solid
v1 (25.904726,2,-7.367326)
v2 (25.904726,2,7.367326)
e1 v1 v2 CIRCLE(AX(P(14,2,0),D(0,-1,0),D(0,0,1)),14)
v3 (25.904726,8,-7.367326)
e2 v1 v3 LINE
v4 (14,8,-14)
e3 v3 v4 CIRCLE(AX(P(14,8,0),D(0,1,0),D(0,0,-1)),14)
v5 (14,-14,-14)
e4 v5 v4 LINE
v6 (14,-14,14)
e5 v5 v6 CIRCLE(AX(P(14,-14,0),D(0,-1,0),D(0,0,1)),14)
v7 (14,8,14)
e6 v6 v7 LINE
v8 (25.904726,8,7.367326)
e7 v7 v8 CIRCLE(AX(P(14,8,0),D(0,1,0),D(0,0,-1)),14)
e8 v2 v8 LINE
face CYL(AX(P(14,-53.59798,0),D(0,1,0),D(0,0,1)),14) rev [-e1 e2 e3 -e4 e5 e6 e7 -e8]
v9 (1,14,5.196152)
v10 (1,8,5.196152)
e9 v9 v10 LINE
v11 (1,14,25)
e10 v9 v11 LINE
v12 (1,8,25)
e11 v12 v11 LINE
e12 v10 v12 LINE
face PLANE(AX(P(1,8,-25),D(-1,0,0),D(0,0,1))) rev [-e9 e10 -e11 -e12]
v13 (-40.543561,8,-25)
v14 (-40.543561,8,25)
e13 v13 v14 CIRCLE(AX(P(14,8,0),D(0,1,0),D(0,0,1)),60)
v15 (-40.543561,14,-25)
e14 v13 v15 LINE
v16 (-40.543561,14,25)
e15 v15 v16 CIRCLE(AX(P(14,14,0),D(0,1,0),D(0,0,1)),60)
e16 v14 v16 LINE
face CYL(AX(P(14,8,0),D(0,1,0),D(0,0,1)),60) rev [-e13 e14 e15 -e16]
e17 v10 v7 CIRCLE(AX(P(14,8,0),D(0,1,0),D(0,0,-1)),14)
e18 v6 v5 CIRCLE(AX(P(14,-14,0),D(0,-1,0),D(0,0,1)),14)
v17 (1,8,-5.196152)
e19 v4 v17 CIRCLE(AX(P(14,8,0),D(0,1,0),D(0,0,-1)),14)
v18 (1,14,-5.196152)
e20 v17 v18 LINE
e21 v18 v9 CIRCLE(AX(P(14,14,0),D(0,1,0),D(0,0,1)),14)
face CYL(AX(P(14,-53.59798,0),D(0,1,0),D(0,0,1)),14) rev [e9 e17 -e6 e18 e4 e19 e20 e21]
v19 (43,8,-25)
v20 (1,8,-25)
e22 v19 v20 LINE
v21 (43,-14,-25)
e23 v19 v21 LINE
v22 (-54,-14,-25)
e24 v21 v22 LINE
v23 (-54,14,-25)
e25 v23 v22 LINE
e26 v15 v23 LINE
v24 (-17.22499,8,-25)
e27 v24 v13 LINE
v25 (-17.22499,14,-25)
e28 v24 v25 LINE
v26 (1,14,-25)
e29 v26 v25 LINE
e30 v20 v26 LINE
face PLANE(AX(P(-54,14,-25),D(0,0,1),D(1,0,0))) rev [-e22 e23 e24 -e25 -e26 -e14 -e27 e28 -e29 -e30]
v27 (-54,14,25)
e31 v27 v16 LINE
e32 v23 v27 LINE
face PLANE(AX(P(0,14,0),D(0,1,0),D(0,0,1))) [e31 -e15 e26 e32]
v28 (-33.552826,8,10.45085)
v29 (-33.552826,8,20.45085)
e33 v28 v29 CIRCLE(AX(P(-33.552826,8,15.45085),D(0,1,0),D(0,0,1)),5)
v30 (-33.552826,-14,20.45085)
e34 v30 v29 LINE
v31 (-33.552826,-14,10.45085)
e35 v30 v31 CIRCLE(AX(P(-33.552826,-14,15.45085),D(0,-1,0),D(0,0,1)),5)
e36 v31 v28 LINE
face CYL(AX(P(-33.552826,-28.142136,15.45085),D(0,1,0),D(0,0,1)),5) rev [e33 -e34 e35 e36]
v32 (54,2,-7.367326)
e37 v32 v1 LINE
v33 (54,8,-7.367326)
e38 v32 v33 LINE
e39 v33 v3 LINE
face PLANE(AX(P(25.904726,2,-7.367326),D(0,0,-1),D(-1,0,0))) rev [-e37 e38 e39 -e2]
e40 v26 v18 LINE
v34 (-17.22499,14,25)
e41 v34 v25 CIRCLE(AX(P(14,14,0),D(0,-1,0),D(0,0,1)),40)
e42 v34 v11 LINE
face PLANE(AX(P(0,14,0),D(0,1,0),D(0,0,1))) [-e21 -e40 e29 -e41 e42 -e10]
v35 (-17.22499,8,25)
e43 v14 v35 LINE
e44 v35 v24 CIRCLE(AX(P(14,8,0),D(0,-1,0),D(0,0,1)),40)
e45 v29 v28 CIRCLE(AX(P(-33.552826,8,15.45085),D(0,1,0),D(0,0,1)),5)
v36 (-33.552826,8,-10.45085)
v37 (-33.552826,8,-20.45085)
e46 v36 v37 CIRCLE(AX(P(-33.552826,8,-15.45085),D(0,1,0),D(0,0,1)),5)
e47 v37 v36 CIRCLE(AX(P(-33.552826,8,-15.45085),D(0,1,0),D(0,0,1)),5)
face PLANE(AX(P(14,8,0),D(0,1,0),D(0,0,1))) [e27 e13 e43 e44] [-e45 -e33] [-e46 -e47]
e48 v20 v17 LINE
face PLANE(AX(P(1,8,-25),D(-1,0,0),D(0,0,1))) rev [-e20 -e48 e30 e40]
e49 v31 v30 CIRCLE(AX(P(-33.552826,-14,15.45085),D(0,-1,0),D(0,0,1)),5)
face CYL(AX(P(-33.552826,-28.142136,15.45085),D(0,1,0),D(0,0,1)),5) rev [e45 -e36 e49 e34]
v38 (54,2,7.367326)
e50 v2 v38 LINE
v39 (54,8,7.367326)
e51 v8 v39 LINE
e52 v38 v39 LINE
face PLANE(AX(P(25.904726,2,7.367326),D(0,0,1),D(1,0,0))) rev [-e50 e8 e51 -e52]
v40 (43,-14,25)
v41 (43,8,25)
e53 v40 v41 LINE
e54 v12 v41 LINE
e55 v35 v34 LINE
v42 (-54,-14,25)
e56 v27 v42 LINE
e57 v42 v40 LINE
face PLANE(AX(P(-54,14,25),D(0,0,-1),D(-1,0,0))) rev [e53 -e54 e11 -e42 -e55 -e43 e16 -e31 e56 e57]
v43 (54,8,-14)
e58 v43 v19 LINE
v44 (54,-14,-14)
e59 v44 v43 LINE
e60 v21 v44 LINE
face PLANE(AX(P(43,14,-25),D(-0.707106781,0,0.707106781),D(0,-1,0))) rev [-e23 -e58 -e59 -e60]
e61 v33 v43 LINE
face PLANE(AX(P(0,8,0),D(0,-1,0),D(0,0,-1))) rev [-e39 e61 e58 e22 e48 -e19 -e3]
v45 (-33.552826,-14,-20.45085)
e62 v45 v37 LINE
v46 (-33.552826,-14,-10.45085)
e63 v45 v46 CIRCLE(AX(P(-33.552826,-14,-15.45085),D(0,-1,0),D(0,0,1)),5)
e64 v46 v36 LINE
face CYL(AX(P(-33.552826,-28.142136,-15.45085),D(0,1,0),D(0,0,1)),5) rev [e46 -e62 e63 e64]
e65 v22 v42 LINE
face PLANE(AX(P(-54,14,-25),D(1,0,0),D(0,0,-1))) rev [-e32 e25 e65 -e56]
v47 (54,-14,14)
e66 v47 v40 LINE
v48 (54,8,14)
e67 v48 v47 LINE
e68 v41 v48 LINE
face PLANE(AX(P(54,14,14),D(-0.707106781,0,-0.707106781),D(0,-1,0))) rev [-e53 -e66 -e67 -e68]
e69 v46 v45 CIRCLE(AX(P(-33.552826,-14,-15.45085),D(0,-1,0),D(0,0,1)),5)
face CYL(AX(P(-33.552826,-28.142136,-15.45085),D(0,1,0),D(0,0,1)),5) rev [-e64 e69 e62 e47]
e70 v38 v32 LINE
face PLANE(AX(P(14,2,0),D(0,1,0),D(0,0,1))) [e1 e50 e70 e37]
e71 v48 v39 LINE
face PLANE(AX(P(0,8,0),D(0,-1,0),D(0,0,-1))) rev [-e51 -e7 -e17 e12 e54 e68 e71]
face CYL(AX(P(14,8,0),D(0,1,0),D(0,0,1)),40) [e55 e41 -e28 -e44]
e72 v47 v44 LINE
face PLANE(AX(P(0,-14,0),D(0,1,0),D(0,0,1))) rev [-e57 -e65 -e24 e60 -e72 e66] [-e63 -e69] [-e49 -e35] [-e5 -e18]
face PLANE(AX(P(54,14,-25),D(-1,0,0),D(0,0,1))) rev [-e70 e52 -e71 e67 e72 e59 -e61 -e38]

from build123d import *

# Parameters (mm, degrees)
BASE_BLOCK_SKETCH_W        = 108
BASE_BLOCK_SKETCH_H        = 50
BASE_BLOCK_108X50X28_DEPTH = 14
END_CHAMFER_11X45DEG_SIZE  = 11
THROUGH_BORE_SKETCH_R      = 14
THROUGH_BORE_DEPTH         = 28
SLOT_RECESS_6_DEEP_DEPTH   = 6
ARC_RECESS_6_DEEP_DEPTH    = 6
ARC_HOLES_SKETCH_R         = 5
HOLES_2XD10_ON_R100_DEPTH  = 22
GROOVE_6_DEEP_DEPTH        = 6


with BuildPart() as part:
    # Base Block Sketch → Base Block 108x50x28 (new, symmetric)
    with BuildSketch(Plane(origin=(0, 0, 0), x_dir=(1, 0, 0), z_dir=(0, 1, 0))):
        Rectangle(BASE_BLOCK_SKETCH_W, BASE_BLOCK_SKETCH_H)
    extrude(amount=BASE_BLOCK_108X50X28_DEPTH, both=True)

    # End Chamfer 11x45deg
    end_chamfer_11x45deg_edges = [part.edges().sort_by_distance(p)[0] for p in [
        (54, 0, 25),
        (54, 0, -25),
    ]]
    chamfer(end_chamfer_11x45deg_edges, length=END_CHAMFER_11X45DEG_SIZE)

    # Through Bore Sketch → Through Bore (cut)
    with BuildSketch(Plane(origin=(0, 14, 0), x_dir=(1, 0, 0), z_dir=(0, 1, 0))):
        with Locations(Location((14, 0, 0), (0, 0, 270))):
            Circle(THROUGH_BORE_SKETCH_R)
    extrude(amount=-THROUGH_BORE_DEPTH, mode=Mode.SUBTRACT)

    # Slot Recess Sketch → Slot Recess 6 Deep (cut)
    with BuildSketch(Plane(origin=(0, 14, 0), x_dir=(1, 0, 0), z_dir=(0, 1, 0))):
        Polygon((1, 25), (1, -25), (43, -25), (54, -14), (54, 14), (43, 25), align=None)
    extrude(amount=-SLOT_RECESS_6_DEEP_DEPTH, mode=Mode.SUBTRACT)

    # Arc Recess Sketch → Arc Recess 6 Deep (cut)
    with BuildSketch(Plane(origin=(0, 14, 0), x_dir=(1, 0, 0), z_dir=(0, 1, 0))):
        with BuildLine():
            Line((-40.543560573, -25), (-17.224989992, -25))
            ThreePointArc((-17.224989992, -25), (-26, 0), (-17.224989992, 25))
            Line((-17.224989992, 25), (-40.543560573, 25))
            ThreePointArc((-40.543560573, 25), (-46, 0), (-40.543560573, -25))
        make_face()
    extrude(amount=-ARC_RECESS_6_DEEP_DEPTH, mode=Mode.SUBTRACT)

    # Arc Holes Sketch → Holes 2xD10 on R100 (cut)
    with BuildSketch(Plane(origin=(0, 8, 0), x_dir=(1, 0, 0), z_dir=(0, 1, 0))):
        with Locations(Location((-33.552825815, 15.450849719, 0), (0, 0, 270))):
            Circle(ARC_HOLES_SKETCH_R)
        with Locations(Location((-33.552825815, -15.450849719, 0), (0, 0, 270))):
            Circle(ARC_HOLES_SKETCH_R)
    extrude(amount=-HOLES_2XD10_ON_R100_DEPTH, mode=Mode.SUBTRACT)

    # Groove Sketch → Groove 6 Deep (cut)
    with BuildSketch(Plane(origin=(0, 8, 0), x_dir=(1, 0, 0), z_dir=(0, 1, 0))):
        with BuildLine():
            Line((25.904726429, 7.367325747), (54, 7.367325747))
            Line((54, 7.367325747), (54, -7.367325747))
            Line((54, -7.367325747), (25.904726429, -7.367325747))
            ThreePointArc((25.904726429, -7.367325747), (28, 0), (25.904726429, 7.367325747))
        make_face()
    extrude(amount=-GROOVE_6_DEEP_DEPTH, mode=Mode.SUBTRACT)


solid = part.part
